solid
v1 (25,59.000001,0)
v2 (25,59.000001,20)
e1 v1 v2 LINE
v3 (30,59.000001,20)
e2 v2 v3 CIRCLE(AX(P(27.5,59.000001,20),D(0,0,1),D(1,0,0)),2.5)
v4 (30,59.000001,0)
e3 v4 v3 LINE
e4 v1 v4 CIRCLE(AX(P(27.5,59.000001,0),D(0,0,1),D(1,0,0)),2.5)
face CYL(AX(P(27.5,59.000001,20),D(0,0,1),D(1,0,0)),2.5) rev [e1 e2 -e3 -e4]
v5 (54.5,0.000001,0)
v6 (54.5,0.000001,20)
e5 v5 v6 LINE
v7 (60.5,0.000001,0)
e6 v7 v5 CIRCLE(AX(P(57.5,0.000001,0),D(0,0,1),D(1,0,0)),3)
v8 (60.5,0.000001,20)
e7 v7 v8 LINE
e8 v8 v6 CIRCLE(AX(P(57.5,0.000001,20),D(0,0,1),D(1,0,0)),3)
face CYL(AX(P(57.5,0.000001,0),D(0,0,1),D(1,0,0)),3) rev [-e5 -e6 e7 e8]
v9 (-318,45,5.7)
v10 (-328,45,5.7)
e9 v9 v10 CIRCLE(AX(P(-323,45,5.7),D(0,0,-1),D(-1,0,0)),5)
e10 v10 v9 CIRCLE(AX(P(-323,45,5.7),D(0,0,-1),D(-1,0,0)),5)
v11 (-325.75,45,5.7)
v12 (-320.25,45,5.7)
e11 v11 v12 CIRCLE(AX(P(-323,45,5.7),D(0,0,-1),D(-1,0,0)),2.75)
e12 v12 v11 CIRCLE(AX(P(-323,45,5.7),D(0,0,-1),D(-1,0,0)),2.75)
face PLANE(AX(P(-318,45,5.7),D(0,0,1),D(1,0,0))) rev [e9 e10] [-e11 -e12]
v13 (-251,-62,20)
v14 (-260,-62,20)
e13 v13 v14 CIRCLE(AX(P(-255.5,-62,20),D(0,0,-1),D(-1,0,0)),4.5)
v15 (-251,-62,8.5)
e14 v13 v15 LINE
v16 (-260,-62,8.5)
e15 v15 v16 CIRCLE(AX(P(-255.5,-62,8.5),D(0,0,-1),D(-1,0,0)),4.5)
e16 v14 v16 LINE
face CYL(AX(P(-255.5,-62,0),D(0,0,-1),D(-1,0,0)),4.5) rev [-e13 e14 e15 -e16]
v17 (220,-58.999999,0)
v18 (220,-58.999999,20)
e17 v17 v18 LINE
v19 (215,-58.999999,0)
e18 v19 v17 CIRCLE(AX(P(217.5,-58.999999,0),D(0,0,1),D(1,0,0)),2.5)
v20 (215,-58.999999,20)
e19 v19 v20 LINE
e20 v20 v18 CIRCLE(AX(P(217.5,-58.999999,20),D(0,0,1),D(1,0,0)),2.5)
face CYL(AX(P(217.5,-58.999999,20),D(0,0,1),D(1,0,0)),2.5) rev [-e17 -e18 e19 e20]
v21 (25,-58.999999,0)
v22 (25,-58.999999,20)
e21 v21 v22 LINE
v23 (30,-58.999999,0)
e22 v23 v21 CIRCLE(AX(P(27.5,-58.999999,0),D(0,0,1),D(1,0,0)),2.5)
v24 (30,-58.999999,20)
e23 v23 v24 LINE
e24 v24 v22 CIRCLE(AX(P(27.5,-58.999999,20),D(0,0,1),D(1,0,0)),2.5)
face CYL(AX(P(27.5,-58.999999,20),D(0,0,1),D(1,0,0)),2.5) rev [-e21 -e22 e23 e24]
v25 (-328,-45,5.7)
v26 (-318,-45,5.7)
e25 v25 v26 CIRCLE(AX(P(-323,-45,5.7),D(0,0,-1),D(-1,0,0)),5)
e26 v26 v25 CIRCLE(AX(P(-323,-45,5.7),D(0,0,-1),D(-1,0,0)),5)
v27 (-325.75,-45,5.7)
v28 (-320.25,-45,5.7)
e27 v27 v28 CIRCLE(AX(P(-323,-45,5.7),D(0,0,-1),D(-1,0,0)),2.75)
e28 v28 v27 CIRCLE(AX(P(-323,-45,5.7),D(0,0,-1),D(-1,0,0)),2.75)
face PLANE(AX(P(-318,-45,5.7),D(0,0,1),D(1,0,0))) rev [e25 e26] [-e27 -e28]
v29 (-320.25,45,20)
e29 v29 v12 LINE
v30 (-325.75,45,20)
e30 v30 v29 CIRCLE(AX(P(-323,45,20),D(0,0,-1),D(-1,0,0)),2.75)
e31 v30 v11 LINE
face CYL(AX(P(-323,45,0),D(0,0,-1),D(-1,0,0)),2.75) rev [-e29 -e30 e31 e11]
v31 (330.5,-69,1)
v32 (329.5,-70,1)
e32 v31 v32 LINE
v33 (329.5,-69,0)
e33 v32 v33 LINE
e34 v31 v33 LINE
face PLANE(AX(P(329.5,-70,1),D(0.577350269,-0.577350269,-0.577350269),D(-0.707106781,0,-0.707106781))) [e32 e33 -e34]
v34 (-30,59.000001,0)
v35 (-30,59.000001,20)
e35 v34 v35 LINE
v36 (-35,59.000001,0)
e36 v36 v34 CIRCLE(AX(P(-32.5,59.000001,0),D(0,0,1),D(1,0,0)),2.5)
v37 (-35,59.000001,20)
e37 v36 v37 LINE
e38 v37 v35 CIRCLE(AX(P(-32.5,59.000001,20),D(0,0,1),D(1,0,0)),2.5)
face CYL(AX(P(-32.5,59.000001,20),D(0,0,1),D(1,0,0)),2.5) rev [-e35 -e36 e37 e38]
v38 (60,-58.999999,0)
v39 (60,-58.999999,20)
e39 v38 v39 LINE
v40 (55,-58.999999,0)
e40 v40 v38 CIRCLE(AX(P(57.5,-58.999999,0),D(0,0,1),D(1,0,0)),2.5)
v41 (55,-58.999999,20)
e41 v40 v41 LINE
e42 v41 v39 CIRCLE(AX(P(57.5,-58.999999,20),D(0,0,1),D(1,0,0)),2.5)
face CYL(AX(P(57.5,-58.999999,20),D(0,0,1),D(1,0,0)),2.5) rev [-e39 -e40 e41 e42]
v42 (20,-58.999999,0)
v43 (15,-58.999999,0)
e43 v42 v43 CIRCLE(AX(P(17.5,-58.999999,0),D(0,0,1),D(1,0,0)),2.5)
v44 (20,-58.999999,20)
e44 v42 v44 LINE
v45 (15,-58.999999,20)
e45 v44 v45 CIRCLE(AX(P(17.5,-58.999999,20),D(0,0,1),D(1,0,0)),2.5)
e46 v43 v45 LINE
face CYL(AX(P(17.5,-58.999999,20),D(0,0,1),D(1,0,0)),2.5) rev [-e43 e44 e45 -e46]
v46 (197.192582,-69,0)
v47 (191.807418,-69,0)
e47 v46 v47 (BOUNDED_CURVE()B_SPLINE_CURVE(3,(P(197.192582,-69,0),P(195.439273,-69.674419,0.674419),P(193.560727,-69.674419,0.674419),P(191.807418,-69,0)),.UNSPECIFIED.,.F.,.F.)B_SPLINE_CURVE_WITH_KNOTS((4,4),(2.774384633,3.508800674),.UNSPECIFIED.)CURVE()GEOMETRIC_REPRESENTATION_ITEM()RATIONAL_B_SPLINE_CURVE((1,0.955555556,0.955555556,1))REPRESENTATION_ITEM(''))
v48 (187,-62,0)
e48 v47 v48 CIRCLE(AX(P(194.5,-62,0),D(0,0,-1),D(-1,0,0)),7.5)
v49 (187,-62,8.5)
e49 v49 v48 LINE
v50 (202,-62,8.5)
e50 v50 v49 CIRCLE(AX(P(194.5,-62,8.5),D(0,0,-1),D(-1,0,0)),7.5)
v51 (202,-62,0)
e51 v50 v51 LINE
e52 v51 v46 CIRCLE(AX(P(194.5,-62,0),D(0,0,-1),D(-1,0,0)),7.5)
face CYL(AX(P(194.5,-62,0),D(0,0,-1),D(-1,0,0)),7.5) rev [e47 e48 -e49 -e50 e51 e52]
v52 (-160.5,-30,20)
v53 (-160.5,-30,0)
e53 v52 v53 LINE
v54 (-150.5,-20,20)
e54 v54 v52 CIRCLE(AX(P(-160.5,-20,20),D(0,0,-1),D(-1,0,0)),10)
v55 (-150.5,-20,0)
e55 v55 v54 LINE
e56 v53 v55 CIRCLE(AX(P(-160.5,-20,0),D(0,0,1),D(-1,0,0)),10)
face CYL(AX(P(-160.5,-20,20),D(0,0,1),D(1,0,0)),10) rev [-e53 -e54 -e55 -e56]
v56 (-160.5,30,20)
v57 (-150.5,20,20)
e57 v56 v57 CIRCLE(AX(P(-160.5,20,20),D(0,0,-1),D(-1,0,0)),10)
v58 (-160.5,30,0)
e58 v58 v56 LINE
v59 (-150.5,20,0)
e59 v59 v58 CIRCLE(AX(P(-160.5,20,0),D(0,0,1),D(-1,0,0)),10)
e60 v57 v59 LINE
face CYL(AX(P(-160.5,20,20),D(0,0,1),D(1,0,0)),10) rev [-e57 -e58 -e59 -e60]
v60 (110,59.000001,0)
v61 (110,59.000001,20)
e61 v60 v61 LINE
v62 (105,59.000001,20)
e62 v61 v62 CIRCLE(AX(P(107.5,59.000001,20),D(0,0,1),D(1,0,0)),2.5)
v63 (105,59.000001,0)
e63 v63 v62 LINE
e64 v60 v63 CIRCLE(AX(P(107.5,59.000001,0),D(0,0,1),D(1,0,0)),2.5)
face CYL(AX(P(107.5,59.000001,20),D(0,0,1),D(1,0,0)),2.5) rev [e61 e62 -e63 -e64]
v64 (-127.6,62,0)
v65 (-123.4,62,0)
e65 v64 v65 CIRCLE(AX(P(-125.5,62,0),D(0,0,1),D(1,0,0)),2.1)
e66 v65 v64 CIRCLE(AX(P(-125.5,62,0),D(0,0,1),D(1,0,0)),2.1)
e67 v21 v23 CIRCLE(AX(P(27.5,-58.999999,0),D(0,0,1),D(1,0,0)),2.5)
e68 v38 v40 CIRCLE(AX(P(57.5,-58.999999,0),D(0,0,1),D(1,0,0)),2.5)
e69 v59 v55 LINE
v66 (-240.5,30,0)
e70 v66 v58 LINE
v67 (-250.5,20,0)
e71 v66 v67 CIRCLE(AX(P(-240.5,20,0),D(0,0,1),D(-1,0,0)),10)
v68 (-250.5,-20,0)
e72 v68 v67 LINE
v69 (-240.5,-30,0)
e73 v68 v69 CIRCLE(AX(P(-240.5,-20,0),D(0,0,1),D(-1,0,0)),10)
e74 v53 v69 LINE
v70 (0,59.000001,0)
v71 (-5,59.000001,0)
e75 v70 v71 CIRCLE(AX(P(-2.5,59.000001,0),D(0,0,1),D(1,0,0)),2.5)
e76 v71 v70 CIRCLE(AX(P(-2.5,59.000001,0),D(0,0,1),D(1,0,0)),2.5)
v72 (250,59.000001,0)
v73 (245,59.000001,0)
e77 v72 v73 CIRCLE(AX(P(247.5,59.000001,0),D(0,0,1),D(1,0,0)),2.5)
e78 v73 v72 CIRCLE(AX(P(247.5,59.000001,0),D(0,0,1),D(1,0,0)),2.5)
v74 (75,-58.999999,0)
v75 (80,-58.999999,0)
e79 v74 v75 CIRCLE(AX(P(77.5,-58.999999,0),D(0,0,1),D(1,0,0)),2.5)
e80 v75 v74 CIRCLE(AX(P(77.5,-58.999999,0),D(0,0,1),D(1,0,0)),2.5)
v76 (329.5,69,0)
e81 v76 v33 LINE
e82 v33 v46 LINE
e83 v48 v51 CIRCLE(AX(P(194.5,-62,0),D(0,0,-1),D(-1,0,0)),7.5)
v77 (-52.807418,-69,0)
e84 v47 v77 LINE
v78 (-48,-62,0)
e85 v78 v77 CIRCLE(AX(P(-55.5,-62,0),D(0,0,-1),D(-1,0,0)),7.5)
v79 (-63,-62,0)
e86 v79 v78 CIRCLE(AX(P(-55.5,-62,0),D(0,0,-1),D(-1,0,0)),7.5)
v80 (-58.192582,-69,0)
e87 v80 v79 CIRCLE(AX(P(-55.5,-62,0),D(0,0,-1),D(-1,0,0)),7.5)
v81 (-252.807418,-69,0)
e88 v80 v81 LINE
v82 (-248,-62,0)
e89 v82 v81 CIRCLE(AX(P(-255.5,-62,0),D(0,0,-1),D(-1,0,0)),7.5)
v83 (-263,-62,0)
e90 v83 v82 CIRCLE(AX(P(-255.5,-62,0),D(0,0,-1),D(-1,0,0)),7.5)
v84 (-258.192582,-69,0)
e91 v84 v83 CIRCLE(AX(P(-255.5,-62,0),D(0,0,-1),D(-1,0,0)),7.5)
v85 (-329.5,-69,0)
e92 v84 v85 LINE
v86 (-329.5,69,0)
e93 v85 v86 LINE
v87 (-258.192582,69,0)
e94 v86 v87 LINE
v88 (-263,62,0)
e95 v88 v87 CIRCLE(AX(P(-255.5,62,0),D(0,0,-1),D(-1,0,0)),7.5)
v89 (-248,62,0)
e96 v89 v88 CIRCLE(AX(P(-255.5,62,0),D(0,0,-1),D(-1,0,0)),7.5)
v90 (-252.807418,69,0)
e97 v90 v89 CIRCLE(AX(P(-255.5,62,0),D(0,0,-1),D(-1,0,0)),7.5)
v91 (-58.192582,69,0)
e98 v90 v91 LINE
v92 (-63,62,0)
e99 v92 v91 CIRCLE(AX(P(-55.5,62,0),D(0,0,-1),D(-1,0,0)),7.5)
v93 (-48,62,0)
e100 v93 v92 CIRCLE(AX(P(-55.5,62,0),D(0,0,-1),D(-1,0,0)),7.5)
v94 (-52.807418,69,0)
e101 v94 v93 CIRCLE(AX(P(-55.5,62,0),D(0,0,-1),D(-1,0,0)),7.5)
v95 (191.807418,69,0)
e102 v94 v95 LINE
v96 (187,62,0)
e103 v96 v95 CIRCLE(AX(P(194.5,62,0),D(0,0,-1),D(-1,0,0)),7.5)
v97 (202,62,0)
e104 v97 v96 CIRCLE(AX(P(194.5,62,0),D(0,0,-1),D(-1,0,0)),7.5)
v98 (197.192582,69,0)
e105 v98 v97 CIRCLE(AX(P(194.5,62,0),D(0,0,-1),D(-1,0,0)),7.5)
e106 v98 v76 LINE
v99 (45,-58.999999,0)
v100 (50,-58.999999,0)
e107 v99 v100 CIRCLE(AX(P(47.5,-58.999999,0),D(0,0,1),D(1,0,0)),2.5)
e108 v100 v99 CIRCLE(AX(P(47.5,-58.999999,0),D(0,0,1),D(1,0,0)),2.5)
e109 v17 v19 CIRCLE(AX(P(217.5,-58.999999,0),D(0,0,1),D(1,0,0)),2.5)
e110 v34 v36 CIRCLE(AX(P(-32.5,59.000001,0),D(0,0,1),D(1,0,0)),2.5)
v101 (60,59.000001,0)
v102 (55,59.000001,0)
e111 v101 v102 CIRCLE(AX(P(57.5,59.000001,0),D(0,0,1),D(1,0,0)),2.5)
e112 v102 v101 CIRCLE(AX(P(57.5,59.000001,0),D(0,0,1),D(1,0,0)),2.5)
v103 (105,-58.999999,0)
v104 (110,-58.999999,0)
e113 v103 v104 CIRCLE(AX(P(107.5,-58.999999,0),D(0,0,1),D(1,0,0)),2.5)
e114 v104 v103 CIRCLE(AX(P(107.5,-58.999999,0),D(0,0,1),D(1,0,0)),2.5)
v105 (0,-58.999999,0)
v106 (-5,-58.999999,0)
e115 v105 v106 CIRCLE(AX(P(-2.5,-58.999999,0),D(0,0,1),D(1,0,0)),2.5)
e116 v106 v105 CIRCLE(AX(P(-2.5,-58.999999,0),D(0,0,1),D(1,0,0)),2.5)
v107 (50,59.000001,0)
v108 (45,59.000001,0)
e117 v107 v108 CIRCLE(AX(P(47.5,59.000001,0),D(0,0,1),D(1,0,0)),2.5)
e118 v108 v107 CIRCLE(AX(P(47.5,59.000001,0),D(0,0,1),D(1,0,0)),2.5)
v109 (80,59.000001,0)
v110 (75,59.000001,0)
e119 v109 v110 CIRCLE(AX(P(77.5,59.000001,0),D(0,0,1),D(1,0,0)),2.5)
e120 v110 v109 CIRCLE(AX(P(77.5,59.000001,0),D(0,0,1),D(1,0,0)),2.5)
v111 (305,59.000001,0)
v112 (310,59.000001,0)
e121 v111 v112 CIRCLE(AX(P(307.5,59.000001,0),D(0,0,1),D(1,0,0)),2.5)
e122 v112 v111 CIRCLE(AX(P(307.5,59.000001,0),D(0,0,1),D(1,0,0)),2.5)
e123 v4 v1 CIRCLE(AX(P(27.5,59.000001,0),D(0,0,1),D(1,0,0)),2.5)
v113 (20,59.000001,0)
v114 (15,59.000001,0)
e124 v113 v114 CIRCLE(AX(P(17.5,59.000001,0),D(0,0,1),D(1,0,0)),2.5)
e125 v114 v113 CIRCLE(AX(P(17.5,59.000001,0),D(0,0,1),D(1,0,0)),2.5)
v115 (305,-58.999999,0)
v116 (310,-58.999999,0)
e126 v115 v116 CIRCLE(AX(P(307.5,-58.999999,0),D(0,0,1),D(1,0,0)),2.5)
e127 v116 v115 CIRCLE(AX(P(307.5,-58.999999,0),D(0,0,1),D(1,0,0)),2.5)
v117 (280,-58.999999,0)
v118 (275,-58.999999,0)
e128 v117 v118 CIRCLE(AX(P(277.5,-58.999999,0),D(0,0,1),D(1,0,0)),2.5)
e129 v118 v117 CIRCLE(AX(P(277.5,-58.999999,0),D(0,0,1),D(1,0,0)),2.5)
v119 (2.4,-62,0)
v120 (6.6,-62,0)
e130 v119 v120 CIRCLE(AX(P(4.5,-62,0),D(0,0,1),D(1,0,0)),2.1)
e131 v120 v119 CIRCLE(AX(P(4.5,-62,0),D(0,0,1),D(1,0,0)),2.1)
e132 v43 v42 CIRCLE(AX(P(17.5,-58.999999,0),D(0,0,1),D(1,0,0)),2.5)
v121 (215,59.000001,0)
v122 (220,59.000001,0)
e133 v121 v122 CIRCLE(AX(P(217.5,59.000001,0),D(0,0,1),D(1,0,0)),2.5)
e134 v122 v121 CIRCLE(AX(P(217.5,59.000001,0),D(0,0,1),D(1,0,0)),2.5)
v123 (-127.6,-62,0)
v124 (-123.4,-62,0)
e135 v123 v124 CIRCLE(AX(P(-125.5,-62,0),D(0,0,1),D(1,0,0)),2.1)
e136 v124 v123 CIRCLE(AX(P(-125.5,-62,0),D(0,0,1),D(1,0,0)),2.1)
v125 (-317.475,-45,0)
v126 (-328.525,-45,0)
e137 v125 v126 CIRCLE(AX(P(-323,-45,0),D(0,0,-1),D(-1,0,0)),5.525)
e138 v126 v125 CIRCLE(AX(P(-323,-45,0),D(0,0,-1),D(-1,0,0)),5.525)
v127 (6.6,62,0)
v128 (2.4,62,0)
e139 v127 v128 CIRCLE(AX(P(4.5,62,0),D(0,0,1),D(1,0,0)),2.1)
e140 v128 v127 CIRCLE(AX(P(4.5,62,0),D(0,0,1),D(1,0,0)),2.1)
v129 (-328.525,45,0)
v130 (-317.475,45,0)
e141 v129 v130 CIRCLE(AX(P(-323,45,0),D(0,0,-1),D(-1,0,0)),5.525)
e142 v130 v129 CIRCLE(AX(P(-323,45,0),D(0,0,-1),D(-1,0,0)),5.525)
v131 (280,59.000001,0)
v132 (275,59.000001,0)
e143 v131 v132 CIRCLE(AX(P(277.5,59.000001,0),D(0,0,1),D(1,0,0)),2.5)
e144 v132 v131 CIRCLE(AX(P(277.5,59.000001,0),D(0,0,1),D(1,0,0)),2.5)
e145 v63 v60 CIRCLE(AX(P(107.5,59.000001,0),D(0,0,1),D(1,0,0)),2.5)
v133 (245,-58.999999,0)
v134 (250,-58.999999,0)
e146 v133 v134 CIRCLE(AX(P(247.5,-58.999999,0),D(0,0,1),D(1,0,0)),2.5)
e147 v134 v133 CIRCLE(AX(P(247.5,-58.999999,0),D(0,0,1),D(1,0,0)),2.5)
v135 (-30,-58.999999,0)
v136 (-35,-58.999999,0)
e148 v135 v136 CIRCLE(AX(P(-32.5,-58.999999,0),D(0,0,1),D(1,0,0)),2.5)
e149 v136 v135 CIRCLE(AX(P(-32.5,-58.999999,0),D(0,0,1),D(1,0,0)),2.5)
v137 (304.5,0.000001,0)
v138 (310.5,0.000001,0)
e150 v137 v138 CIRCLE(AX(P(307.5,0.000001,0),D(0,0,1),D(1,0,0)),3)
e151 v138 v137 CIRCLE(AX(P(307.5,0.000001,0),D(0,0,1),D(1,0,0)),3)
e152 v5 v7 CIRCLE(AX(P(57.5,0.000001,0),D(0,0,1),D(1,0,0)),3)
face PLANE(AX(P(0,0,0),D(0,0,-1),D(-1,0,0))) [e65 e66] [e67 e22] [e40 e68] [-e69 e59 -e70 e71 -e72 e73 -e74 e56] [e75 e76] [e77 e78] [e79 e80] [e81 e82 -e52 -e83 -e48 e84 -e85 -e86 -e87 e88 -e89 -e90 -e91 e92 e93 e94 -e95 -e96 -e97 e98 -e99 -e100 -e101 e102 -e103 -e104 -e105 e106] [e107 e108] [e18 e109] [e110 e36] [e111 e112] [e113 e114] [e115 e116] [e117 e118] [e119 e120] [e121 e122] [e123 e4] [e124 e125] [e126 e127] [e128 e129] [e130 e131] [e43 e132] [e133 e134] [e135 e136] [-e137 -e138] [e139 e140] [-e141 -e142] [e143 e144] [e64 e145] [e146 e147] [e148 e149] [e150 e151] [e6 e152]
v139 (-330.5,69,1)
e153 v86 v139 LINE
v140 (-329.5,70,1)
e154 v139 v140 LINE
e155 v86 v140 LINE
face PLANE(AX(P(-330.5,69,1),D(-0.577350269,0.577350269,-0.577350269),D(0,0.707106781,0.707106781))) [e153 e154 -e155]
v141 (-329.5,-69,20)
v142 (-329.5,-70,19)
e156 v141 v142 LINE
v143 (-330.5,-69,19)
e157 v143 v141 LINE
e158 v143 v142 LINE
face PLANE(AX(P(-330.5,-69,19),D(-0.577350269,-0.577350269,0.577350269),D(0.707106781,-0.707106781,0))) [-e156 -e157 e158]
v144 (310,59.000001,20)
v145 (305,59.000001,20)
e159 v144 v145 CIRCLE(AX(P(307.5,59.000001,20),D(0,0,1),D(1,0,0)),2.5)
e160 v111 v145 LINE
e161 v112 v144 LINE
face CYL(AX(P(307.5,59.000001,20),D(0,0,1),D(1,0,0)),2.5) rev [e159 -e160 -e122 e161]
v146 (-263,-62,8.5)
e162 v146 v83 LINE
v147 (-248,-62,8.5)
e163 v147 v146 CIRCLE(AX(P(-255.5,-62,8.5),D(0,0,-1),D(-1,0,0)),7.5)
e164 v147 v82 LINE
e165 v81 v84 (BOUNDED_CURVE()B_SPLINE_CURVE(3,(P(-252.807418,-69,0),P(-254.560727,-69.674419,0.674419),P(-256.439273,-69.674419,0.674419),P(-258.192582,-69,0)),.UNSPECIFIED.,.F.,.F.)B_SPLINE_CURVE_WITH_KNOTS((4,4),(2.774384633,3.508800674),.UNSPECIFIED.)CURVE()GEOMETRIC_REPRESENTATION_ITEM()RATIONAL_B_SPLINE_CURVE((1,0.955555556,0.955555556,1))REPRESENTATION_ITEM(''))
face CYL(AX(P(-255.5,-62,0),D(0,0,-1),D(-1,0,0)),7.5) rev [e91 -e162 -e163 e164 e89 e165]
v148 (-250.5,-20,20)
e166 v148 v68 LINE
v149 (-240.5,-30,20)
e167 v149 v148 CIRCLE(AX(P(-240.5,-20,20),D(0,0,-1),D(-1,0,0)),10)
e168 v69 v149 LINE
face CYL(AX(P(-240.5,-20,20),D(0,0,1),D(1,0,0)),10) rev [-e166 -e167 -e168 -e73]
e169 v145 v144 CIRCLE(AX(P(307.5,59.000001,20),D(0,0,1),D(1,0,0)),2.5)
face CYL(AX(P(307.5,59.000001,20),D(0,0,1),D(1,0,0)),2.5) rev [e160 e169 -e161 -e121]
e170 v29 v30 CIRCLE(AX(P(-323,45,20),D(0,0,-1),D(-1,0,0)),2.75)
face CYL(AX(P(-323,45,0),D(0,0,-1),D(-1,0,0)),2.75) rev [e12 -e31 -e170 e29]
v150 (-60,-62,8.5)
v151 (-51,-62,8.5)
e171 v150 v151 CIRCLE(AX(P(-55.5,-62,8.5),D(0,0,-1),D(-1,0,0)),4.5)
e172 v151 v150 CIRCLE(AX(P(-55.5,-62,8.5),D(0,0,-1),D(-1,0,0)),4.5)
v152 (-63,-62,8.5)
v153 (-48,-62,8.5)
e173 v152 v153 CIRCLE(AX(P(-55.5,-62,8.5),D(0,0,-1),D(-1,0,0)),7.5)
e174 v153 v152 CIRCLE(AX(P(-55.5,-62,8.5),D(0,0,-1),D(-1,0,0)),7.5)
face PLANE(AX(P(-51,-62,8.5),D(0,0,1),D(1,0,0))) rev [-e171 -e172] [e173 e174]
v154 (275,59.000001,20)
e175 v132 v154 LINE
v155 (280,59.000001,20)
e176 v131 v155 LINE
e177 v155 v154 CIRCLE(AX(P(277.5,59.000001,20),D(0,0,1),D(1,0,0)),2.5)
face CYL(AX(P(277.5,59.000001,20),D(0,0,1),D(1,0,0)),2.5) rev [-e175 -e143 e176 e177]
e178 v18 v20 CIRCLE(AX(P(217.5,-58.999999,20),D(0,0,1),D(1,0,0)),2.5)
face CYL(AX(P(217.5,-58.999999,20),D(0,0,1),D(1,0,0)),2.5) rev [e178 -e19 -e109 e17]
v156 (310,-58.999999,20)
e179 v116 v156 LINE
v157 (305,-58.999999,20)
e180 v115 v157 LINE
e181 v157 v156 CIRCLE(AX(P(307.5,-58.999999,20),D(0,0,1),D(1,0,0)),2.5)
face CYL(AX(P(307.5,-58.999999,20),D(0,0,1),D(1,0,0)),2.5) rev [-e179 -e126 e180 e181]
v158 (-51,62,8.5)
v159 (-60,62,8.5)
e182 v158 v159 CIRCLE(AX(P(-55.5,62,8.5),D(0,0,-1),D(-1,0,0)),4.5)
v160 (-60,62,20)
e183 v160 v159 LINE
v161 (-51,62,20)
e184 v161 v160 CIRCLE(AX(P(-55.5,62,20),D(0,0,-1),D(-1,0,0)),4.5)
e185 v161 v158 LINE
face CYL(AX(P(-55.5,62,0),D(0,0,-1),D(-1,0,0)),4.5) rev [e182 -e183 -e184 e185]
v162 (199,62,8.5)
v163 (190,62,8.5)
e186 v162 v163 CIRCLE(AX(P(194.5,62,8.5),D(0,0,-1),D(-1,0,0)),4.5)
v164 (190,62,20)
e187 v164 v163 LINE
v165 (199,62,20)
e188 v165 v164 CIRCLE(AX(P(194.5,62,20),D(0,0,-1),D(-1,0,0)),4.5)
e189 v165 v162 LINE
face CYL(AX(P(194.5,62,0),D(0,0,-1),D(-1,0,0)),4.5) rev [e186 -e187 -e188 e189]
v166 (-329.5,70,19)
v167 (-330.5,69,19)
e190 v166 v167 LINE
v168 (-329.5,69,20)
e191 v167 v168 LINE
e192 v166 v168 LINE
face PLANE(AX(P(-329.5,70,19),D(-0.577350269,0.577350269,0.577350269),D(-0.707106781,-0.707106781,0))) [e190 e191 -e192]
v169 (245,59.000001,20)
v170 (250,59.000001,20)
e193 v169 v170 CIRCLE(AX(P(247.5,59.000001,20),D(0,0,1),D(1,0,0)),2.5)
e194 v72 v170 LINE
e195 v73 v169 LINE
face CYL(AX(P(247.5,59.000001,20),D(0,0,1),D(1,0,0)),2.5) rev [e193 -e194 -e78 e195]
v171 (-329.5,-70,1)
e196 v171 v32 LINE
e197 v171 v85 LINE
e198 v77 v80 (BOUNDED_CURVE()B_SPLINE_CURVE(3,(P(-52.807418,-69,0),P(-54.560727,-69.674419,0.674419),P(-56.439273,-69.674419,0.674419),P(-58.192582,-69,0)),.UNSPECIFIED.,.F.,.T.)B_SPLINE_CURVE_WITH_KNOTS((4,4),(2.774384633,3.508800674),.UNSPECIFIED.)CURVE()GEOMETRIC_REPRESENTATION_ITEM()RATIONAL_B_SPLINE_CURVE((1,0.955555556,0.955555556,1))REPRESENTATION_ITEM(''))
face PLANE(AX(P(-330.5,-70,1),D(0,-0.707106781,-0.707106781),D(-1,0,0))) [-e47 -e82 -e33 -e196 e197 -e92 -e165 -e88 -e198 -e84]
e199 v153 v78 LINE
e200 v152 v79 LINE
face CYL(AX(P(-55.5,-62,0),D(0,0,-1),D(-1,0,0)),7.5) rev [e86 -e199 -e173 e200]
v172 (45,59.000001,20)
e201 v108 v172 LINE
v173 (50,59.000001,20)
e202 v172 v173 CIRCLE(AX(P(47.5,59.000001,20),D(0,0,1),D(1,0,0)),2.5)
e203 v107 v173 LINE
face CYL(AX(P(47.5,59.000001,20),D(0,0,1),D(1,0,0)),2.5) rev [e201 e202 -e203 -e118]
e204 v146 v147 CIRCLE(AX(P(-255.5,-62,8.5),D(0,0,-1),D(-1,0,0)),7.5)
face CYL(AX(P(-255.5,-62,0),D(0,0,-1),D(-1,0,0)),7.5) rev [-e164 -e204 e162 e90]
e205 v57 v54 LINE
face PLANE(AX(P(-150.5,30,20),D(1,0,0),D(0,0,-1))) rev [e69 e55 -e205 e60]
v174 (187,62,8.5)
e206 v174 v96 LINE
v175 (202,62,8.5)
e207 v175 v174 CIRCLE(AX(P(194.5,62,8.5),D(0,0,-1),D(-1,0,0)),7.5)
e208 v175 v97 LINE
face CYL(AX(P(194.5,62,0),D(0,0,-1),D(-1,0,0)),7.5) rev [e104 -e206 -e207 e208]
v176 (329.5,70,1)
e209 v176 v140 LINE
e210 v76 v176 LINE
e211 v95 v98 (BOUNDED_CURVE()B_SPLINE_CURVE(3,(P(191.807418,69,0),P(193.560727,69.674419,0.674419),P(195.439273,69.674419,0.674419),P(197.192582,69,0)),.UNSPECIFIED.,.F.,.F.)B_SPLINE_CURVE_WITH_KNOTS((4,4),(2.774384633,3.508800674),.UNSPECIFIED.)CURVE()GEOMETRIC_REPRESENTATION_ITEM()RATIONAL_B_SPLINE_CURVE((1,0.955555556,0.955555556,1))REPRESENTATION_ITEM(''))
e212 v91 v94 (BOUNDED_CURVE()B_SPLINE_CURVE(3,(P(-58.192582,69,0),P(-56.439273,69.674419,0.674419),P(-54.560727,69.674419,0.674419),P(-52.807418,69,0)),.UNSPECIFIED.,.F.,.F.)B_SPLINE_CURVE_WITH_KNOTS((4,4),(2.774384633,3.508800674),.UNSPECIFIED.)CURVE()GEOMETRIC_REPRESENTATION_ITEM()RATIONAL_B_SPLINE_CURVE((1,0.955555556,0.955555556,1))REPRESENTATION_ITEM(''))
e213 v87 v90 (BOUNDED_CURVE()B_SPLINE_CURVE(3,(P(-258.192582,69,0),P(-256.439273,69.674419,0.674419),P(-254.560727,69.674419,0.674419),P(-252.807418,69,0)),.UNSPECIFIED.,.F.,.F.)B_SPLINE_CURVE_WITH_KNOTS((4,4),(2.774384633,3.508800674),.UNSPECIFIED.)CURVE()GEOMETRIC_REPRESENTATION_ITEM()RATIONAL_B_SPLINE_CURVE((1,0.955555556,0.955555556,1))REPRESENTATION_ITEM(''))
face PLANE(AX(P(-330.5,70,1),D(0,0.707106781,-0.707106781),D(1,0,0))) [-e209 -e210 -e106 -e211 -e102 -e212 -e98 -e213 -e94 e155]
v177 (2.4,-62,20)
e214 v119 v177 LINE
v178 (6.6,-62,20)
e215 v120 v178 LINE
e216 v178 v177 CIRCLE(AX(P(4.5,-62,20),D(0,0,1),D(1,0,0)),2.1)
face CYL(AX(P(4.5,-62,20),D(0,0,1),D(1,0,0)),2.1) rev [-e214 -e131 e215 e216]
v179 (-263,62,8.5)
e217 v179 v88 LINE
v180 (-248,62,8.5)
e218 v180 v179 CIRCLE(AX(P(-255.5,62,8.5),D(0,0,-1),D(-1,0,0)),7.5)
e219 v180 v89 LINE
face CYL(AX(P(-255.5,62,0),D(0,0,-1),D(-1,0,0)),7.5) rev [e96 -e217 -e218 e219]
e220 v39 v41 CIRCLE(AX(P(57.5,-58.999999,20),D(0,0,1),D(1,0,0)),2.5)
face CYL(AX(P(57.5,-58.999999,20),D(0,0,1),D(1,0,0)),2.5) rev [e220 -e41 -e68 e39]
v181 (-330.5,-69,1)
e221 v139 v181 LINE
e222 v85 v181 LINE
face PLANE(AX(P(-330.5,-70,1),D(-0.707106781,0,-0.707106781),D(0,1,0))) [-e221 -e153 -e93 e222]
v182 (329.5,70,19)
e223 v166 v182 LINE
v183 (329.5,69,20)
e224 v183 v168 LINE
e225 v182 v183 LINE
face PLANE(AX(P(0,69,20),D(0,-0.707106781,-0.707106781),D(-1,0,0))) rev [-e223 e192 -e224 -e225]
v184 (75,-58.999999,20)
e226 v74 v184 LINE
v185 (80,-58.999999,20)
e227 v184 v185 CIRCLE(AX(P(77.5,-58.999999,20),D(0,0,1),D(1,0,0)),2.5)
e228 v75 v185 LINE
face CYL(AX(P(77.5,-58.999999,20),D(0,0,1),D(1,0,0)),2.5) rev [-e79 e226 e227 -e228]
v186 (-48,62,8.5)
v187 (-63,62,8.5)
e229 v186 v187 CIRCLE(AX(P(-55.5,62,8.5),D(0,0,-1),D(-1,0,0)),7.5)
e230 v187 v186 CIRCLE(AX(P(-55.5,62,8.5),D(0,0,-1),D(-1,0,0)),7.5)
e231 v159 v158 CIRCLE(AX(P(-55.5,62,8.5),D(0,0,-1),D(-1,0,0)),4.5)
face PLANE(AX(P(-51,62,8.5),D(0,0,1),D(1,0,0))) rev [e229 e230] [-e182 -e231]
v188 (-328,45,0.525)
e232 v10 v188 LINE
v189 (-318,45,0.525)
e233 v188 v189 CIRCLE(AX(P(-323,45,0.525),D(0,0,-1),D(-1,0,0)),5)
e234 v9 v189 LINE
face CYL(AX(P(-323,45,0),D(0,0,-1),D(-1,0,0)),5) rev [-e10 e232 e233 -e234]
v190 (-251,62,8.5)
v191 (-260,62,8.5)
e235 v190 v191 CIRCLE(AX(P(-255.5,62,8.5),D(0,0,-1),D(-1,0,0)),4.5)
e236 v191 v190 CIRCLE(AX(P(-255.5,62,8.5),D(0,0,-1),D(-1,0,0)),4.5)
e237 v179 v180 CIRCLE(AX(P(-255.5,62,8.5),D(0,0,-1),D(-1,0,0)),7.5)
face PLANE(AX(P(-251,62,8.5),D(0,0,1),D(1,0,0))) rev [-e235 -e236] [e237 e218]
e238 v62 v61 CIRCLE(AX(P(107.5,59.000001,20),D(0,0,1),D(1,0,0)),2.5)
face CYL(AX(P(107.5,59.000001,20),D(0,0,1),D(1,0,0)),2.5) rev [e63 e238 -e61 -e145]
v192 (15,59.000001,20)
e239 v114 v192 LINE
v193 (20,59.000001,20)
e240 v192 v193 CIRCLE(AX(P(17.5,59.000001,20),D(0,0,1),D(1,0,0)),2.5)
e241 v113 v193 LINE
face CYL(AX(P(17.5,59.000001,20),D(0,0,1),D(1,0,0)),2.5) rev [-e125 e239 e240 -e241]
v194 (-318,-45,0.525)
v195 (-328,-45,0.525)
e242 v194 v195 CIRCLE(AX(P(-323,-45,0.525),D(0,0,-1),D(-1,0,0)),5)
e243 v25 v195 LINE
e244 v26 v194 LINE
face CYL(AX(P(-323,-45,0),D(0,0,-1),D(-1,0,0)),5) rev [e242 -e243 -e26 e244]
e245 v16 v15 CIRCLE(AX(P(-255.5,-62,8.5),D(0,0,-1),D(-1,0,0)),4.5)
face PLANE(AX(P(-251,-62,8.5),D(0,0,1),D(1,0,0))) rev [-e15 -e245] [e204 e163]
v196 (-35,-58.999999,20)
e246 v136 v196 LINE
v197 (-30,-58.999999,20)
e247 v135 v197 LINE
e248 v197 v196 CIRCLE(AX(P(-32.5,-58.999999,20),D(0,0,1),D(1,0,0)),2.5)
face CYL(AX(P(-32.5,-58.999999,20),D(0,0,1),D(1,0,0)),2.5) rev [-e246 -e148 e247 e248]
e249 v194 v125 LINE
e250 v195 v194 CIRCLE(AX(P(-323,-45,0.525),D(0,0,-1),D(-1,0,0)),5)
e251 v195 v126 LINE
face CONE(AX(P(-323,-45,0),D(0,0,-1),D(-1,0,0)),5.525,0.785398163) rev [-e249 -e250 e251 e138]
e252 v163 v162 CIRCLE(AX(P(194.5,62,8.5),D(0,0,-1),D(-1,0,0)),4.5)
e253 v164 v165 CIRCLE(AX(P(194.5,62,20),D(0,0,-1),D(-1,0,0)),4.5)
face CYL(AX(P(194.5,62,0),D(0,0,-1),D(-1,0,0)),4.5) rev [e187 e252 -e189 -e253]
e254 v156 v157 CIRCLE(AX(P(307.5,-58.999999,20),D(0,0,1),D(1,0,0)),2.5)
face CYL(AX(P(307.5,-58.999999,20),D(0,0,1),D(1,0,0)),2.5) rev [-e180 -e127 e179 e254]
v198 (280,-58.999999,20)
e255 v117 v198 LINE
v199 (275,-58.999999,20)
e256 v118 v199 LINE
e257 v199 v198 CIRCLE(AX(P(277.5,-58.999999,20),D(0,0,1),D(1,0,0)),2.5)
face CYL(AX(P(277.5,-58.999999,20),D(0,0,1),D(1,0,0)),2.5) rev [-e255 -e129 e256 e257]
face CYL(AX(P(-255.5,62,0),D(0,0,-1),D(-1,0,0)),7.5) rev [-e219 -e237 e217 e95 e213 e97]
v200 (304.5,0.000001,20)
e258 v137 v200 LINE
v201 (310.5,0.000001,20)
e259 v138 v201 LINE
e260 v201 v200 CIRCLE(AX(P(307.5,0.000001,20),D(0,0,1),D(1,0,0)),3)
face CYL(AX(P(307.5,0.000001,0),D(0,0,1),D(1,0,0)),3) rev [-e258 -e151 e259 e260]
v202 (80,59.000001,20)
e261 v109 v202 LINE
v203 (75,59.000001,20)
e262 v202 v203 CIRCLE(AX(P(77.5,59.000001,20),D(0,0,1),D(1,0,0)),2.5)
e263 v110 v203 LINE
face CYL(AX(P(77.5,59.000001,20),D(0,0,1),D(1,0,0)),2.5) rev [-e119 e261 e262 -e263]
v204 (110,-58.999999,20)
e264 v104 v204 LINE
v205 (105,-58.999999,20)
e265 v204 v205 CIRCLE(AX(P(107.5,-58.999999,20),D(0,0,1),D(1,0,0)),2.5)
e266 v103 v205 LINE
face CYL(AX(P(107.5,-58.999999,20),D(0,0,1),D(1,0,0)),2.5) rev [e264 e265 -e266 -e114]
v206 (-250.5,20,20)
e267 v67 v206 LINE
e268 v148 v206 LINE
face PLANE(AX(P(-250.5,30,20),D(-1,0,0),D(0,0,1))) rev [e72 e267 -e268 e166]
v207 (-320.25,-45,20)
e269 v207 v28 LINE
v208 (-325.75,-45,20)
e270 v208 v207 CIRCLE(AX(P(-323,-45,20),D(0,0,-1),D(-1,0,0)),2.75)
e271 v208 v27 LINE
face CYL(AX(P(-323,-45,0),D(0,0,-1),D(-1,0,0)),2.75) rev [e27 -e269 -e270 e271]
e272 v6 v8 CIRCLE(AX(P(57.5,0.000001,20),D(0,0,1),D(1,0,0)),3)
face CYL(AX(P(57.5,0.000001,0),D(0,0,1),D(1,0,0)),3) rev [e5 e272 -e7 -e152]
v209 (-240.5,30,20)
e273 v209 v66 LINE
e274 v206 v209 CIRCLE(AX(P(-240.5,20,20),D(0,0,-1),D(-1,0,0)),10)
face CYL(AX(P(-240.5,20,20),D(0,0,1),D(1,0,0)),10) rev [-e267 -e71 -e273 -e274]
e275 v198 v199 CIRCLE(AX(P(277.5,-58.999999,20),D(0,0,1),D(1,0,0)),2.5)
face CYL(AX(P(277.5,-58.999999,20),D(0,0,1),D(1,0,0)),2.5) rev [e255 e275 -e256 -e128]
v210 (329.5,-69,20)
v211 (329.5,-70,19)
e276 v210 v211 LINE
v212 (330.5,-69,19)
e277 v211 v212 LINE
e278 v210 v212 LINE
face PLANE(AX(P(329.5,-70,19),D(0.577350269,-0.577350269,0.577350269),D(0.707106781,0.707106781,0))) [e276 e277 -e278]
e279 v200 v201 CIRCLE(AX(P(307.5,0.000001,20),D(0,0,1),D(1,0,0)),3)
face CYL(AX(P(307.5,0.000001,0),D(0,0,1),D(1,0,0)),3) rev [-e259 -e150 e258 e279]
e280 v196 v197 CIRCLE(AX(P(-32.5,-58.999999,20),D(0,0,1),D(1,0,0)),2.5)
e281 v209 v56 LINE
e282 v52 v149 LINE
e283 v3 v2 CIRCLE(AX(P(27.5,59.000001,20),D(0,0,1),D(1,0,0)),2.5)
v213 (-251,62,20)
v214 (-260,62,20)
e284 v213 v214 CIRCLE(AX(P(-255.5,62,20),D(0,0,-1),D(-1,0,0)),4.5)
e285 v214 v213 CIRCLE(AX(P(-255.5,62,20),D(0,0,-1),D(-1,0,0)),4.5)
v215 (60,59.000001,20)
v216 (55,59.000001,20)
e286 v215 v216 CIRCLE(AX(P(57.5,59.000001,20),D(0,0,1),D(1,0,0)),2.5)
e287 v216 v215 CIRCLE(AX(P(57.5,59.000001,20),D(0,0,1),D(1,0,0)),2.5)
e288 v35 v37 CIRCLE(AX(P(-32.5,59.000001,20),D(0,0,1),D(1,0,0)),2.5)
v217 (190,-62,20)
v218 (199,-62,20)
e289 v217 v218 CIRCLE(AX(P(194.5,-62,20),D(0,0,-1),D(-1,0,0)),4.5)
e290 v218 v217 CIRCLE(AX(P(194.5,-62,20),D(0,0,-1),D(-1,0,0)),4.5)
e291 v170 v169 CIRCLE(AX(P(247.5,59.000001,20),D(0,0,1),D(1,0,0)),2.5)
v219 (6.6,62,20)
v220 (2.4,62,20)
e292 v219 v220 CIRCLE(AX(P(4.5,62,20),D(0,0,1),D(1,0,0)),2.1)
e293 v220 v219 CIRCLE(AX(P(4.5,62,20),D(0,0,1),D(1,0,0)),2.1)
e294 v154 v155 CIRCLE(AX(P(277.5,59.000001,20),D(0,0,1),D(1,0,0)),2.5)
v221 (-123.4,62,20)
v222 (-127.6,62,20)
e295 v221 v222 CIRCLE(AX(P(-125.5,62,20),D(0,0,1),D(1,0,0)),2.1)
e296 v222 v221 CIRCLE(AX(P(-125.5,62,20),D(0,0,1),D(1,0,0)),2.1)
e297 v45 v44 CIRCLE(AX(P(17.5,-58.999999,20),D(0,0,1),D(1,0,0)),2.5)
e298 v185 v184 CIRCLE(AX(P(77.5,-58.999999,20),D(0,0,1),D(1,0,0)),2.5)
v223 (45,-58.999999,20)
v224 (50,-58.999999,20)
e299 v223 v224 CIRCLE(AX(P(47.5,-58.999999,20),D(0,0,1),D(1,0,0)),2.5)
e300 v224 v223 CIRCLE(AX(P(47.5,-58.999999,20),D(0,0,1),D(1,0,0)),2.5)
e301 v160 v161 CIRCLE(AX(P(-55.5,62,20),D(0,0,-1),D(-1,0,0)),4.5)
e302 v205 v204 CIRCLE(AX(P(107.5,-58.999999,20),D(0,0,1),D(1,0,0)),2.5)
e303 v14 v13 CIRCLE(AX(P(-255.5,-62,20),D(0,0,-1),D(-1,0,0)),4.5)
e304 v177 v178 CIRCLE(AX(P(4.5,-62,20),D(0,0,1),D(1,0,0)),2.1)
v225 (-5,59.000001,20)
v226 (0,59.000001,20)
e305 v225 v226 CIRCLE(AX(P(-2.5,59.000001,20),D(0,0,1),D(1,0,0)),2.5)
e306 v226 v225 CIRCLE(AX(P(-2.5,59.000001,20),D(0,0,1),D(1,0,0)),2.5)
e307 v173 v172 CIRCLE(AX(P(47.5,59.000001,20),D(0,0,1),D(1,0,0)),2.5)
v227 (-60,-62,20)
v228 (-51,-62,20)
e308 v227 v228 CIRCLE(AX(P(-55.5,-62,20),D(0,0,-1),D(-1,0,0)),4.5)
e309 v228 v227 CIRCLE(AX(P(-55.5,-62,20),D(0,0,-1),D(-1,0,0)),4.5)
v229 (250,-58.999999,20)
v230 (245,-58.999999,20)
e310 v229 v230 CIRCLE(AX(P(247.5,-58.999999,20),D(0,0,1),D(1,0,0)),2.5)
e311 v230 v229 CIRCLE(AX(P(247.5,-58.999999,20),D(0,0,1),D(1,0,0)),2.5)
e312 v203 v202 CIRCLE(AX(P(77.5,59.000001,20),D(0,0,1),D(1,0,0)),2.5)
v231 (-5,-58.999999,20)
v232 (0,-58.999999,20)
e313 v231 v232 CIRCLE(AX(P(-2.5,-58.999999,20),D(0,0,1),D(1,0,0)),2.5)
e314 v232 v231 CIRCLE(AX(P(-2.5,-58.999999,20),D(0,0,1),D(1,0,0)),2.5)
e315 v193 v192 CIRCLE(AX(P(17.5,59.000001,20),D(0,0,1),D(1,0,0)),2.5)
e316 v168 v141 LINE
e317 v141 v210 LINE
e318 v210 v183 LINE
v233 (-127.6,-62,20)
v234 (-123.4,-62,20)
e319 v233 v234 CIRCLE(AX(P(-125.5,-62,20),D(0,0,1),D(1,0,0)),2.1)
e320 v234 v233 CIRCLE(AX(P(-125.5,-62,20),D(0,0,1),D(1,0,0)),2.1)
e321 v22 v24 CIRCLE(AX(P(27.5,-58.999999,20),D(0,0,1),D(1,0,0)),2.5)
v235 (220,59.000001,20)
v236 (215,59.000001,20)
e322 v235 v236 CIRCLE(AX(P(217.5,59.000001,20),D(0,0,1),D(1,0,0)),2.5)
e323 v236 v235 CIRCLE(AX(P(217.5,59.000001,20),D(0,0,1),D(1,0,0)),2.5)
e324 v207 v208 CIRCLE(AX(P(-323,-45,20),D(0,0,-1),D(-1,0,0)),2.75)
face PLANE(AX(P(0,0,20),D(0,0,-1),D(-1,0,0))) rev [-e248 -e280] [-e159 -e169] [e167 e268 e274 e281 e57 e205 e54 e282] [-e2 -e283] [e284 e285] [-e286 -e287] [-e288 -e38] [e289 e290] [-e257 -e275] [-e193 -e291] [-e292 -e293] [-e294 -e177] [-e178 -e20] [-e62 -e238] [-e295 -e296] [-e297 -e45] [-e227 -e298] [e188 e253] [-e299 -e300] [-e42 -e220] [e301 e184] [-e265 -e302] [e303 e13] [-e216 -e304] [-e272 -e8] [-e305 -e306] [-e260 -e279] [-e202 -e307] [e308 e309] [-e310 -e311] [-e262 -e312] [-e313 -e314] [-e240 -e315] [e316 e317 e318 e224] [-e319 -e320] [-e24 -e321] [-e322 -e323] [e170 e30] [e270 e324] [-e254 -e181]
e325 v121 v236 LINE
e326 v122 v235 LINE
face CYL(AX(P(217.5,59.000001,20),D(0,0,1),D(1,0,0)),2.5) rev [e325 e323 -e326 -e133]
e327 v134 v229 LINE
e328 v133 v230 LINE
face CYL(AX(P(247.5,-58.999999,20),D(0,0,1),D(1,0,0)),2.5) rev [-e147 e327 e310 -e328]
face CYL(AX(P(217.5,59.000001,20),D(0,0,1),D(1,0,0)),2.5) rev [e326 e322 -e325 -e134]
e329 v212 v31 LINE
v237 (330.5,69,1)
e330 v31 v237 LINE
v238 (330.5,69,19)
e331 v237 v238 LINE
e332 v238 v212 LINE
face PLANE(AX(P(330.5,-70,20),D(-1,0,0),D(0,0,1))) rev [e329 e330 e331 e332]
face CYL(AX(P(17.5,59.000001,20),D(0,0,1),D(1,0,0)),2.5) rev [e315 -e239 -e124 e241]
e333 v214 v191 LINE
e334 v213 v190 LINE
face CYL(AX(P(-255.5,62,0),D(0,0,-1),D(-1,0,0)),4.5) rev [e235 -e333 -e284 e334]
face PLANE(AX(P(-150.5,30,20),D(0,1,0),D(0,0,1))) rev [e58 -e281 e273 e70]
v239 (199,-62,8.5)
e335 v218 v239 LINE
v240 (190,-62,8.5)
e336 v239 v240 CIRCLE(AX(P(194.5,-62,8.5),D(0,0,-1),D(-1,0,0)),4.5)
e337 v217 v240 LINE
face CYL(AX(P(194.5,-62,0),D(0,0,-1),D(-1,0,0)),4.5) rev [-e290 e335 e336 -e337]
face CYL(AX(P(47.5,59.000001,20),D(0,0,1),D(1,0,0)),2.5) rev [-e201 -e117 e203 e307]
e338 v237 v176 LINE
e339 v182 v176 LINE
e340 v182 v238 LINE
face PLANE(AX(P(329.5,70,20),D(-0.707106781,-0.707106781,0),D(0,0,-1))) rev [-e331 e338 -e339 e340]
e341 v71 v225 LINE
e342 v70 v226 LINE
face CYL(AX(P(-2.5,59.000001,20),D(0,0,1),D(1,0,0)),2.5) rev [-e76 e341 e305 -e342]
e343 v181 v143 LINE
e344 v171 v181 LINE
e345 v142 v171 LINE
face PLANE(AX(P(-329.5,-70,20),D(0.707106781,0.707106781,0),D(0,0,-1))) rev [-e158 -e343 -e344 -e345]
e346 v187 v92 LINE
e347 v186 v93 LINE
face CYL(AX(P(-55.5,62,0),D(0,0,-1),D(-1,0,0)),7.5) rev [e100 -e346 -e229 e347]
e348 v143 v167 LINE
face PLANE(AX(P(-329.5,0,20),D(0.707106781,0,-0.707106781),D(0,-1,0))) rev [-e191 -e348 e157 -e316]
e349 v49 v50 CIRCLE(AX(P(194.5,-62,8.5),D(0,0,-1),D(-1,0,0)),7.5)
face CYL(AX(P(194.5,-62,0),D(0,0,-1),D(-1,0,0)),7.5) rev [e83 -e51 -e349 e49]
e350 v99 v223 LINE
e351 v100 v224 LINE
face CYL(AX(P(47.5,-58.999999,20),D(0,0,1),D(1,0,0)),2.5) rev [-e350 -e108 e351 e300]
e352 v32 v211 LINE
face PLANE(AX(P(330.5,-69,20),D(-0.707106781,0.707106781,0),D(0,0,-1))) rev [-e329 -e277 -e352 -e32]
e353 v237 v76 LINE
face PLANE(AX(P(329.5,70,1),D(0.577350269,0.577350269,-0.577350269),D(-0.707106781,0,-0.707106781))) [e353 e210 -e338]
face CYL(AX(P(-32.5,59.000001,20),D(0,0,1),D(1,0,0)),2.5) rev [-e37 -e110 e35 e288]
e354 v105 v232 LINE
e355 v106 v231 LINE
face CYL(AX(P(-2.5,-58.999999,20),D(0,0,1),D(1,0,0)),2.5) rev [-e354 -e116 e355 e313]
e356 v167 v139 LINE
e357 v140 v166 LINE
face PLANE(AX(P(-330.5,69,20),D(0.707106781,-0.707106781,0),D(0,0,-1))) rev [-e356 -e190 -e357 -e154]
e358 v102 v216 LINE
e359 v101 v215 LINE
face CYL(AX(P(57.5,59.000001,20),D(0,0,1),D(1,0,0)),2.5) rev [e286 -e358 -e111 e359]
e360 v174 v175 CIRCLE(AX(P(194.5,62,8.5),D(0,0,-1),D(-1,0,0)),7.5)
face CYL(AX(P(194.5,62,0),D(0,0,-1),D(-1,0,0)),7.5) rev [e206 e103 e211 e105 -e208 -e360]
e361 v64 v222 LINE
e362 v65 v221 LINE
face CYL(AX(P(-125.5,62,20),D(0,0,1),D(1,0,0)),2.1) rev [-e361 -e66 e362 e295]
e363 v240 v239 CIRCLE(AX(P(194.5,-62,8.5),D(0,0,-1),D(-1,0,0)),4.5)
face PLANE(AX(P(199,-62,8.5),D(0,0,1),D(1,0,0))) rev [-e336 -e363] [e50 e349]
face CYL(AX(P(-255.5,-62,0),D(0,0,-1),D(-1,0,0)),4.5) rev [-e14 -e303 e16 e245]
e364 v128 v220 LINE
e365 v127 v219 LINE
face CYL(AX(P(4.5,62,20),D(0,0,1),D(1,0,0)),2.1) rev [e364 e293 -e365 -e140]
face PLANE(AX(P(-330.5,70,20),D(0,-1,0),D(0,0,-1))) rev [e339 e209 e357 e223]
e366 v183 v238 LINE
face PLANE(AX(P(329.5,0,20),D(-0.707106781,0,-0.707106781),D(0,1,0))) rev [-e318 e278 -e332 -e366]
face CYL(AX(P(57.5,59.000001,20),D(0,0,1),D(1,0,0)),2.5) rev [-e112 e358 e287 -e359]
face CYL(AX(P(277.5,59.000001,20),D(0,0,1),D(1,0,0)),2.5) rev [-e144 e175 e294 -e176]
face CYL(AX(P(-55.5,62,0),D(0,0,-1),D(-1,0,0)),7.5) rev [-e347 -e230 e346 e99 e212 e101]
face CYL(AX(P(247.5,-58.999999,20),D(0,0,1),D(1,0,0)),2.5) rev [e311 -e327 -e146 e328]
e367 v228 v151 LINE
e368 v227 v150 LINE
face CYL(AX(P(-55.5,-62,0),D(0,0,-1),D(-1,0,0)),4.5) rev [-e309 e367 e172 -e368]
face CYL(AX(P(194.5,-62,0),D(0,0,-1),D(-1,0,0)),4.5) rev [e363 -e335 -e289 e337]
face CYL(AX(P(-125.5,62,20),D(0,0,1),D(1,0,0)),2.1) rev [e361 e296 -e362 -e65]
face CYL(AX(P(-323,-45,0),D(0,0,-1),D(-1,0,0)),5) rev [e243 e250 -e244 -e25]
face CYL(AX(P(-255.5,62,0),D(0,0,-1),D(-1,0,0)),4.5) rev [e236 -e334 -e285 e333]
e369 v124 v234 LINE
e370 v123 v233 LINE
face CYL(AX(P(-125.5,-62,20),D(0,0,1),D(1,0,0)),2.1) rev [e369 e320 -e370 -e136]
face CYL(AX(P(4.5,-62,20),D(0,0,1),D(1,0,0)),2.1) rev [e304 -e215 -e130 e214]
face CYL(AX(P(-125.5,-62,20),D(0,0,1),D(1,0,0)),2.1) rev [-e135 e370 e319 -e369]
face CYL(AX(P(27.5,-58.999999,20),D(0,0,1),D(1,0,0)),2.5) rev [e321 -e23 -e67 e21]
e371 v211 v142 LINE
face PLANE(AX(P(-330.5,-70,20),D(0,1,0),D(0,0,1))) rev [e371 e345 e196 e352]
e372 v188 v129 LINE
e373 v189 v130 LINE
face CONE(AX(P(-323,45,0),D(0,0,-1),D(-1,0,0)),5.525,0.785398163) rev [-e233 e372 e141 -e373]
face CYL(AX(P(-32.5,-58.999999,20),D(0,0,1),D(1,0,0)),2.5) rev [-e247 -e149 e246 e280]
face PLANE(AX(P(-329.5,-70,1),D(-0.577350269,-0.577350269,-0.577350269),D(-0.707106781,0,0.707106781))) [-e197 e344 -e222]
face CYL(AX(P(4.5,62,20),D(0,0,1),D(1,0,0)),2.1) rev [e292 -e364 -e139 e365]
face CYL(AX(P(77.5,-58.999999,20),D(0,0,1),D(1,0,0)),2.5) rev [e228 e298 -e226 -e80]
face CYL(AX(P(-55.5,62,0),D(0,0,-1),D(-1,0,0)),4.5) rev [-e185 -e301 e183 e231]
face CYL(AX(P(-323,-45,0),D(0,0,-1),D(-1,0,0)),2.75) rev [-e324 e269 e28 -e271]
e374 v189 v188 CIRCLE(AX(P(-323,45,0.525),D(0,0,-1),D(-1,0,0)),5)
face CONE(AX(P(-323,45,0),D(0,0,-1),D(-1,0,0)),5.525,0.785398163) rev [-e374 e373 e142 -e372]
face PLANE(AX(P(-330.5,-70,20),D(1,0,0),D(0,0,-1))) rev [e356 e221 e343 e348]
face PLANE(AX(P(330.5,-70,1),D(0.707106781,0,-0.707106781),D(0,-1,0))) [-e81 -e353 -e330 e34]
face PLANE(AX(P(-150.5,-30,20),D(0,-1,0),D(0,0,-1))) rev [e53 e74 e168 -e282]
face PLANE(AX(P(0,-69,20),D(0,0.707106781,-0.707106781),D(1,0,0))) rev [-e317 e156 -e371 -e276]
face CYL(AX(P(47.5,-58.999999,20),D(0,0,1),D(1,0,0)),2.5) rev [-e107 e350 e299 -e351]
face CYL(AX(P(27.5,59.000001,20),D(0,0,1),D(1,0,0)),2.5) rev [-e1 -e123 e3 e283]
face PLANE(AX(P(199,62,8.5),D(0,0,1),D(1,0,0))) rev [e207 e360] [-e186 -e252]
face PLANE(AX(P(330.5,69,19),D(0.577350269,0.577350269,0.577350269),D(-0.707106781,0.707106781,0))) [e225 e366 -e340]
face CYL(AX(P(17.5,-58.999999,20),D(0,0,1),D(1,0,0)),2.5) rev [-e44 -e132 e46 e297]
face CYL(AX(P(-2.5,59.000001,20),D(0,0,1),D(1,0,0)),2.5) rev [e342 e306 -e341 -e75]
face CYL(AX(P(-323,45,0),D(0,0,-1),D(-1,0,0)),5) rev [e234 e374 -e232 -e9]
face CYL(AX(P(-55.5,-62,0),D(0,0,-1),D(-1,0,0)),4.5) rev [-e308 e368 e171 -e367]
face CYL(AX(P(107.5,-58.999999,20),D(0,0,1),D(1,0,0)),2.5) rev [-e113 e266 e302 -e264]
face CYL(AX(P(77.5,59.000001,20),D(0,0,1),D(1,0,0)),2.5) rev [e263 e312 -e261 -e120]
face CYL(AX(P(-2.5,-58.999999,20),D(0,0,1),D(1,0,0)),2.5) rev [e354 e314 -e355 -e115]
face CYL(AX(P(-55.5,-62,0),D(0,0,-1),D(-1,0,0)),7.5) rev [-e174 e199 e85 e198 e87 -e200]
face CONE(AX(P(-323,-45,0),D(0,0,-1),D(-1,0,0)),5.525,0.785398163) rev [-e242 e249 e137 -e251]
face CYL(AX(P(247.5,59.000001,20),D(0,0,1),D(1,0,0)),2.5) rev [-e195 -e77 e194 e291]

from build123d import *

# Parameters (mm, degrees)
SKETCH_1_W               = 661
SKETCH_1_H               = 140
EXTRUDE_1_DEPTH          = 20
CHAMFER_1_SIZE           = 1
HOLE_WIZARD_M5_1_D       = 4.2
HOLE_WIZARD_M6_1_D       = 5
SKETCH_18_R              = 3
CUT_EXTRUDE_4_DEPTH      = 339.42318183
HOLE_WIZARD_1_AT_2_COUNT = 2
HOLE_WIZARD_1_AT_2_PITCH = 90
HOLE1_D                  = 9
HOLE1_CBORE_D            = 15
HOLE1_CBORE_DEPTH        = 8.5
SKETCH_21_W              = 100
SKETCH_21_H              = 60
CUT_EXTRUDE_5_DEPTH      = 339.42318183
FILLET_2_R               = 10


with BuildPart() as part:
    # 草图1 → 凸台-拉伸1 (new body)
    with BuildSketch(Plane.XY):
        Rectangle(SKETCH_1_W, SKETCH_1_H)
    extrude(amount=EXTRUDE_1_DEPTH)

    # 倒角1
    chamfer_1_edges = [part.edges().sort_by_distance(p)[0] for p in [
        (-330.5, 0, 20),
        (0, -70, 20),
        (330.5, 0, 20),
        (0, -70, 0),
        (-330.5, 0, 0),
        (0, 70, 0),
        (330.5, 0, 0),
        (0, 70, 20),
        (330.5, -70, 10),
        (-330.5, -70, 10),
        (-330.5, 70, 10),
        (330.5, 70, 10),
    ]]
    chamfer(chamfer_1_edges, length=CHAMFER_1_SIZE)

    # M5 螺纹孔1 (through all)
    with Locations(Plane.XY.offset(20)):
        with Locations((4.5, 62), (4.5, -62), (-125.5, 62), (-125.5, -62), (-255.5, -62), (-255.5, 62)):
            Hole(HOLE_WIZARD_M5_1_D / 2)

    # M6 螺纹孔1 (through all)
    with Locations(Plane.XY.offset(20)):
        with Locations((307.5, -58.999999026), (107.5, -58.999999026), (57.5, -58.999999026), (57.5, 59.000000974), (107.5, 59.000000974), (307.5, 59.000000974), (277.5, -58.999999026), (77.5, -58.999999026), (27.5, -58.999999026), (27.5, 59.000000974), (77.5, 59.000000974), (277.5, 59.000000974), (247.5, -58.999999026), (47.5, -58.999999026), (-2.5, -58.999999026), (-2.5, 59.000000974), (47.5, 59.000000974), (247.5, 59.000000974), (217.5, -58.999999026), (17.5, -58.999999026), (-32.5, -58.999999026), (-32.5, 59.000000974), (17.5, 59.000000974), (217.5, 59.000000974)):
            Hole(HOLE_WIZARD_M6_1_D / 2)

    # 草图18 → 切除-拉伸4 (cut, through all)
    with BuildSketch(Plane.XY.offset(20)):
        with Locations((307.5, 9.74e-07)):
            Circle(SKETCH_18_R)
        with Locations((57.5, 9.74e-07)):
            Circle(SKETCH_18_R)
    extrude(amount=-CUT_EXTRUDE_4_DEPTH, mode=Mode.SUBTRACT)

    # 草图20 → 打孔尺寸(%根据)内六角圆柱头螺钉的类型1 (revolve, cut)
    with BuildSketch(Plane(origin=(-323, 45, 0), x_dir=(0, 1, 0), z_dir=(1, 0, 0))):
        Polygon((0, 0), (0, 20), (2.75, 20), (2.75, 5.7), (5, 5.7), (5, 0.525), (5.525, 0), align=None)
    hole_wizard_1 = revolve(axis=Axis((-323, 45, -6.35), (0, 0, 1)), mode=Mode.SUBTRACT)

    # 打孔尺寸(%根据)内六角圆柱头螺钉的类型1 at 2: 打孔尺寸(%根据)内六角圆柱头螺钉的类型1 ×2
    with Locations(*[(0, -i * HOLE_WIZARD_1_AT_2_PITCH, 0) for i in range(1, HOLE_WIZARD_1_AT_2_COUNT)]):
        add(hole_wizard_1, mode=Mode.SUBTRACT)

    # Hole1 (through all)
    with Locations(Plane(origin=(-242.630892878, -61.065000019, 0), x_dir=(-1, 0, 0), z_dir=(0, 0, -1))):
        with Locations((12.869107122, -0.934999981), (-187.130892878, -0.934999981), (-437.130892878, -0.934999981), (-437.130892878, 123.065000019), (-187.130892878, 123.065000019), (12.869107122, 123.065000019)):
            CounterBoreHole(HOLE1_D / 2, HOLE1_CBORE_D / 2, HOLE1_CBORE_DEPTH)

    # 草图21 → 切除-拉伸5 (cut, through all)
    with BuildSketch(Plane(origin=(0, 0, 0), x_dir=(-1, 0, 0), z_dir=(0, 0, -1))):
        with Locations((200.5, 0)):
            Rectangle(SKETCH_21_W, SKETCH_21_H)
    extrude(amount=-CUT_EXTRUDE_5_DEPTH, mode=Mode.SUBTRACT)

    # 圆角2
    fillet_2_edges = [part.edges().sort_by_distance(p)[0] for p in [
        (-150.5, -30, 10),
        (-150.5, 30, 10),
        (-250.5, 30, 10),
        (-250.5, -30, 10),
    ]]
    fillet(fillet_2_edges, radius=FILLET_2_R)


solid = part.part
